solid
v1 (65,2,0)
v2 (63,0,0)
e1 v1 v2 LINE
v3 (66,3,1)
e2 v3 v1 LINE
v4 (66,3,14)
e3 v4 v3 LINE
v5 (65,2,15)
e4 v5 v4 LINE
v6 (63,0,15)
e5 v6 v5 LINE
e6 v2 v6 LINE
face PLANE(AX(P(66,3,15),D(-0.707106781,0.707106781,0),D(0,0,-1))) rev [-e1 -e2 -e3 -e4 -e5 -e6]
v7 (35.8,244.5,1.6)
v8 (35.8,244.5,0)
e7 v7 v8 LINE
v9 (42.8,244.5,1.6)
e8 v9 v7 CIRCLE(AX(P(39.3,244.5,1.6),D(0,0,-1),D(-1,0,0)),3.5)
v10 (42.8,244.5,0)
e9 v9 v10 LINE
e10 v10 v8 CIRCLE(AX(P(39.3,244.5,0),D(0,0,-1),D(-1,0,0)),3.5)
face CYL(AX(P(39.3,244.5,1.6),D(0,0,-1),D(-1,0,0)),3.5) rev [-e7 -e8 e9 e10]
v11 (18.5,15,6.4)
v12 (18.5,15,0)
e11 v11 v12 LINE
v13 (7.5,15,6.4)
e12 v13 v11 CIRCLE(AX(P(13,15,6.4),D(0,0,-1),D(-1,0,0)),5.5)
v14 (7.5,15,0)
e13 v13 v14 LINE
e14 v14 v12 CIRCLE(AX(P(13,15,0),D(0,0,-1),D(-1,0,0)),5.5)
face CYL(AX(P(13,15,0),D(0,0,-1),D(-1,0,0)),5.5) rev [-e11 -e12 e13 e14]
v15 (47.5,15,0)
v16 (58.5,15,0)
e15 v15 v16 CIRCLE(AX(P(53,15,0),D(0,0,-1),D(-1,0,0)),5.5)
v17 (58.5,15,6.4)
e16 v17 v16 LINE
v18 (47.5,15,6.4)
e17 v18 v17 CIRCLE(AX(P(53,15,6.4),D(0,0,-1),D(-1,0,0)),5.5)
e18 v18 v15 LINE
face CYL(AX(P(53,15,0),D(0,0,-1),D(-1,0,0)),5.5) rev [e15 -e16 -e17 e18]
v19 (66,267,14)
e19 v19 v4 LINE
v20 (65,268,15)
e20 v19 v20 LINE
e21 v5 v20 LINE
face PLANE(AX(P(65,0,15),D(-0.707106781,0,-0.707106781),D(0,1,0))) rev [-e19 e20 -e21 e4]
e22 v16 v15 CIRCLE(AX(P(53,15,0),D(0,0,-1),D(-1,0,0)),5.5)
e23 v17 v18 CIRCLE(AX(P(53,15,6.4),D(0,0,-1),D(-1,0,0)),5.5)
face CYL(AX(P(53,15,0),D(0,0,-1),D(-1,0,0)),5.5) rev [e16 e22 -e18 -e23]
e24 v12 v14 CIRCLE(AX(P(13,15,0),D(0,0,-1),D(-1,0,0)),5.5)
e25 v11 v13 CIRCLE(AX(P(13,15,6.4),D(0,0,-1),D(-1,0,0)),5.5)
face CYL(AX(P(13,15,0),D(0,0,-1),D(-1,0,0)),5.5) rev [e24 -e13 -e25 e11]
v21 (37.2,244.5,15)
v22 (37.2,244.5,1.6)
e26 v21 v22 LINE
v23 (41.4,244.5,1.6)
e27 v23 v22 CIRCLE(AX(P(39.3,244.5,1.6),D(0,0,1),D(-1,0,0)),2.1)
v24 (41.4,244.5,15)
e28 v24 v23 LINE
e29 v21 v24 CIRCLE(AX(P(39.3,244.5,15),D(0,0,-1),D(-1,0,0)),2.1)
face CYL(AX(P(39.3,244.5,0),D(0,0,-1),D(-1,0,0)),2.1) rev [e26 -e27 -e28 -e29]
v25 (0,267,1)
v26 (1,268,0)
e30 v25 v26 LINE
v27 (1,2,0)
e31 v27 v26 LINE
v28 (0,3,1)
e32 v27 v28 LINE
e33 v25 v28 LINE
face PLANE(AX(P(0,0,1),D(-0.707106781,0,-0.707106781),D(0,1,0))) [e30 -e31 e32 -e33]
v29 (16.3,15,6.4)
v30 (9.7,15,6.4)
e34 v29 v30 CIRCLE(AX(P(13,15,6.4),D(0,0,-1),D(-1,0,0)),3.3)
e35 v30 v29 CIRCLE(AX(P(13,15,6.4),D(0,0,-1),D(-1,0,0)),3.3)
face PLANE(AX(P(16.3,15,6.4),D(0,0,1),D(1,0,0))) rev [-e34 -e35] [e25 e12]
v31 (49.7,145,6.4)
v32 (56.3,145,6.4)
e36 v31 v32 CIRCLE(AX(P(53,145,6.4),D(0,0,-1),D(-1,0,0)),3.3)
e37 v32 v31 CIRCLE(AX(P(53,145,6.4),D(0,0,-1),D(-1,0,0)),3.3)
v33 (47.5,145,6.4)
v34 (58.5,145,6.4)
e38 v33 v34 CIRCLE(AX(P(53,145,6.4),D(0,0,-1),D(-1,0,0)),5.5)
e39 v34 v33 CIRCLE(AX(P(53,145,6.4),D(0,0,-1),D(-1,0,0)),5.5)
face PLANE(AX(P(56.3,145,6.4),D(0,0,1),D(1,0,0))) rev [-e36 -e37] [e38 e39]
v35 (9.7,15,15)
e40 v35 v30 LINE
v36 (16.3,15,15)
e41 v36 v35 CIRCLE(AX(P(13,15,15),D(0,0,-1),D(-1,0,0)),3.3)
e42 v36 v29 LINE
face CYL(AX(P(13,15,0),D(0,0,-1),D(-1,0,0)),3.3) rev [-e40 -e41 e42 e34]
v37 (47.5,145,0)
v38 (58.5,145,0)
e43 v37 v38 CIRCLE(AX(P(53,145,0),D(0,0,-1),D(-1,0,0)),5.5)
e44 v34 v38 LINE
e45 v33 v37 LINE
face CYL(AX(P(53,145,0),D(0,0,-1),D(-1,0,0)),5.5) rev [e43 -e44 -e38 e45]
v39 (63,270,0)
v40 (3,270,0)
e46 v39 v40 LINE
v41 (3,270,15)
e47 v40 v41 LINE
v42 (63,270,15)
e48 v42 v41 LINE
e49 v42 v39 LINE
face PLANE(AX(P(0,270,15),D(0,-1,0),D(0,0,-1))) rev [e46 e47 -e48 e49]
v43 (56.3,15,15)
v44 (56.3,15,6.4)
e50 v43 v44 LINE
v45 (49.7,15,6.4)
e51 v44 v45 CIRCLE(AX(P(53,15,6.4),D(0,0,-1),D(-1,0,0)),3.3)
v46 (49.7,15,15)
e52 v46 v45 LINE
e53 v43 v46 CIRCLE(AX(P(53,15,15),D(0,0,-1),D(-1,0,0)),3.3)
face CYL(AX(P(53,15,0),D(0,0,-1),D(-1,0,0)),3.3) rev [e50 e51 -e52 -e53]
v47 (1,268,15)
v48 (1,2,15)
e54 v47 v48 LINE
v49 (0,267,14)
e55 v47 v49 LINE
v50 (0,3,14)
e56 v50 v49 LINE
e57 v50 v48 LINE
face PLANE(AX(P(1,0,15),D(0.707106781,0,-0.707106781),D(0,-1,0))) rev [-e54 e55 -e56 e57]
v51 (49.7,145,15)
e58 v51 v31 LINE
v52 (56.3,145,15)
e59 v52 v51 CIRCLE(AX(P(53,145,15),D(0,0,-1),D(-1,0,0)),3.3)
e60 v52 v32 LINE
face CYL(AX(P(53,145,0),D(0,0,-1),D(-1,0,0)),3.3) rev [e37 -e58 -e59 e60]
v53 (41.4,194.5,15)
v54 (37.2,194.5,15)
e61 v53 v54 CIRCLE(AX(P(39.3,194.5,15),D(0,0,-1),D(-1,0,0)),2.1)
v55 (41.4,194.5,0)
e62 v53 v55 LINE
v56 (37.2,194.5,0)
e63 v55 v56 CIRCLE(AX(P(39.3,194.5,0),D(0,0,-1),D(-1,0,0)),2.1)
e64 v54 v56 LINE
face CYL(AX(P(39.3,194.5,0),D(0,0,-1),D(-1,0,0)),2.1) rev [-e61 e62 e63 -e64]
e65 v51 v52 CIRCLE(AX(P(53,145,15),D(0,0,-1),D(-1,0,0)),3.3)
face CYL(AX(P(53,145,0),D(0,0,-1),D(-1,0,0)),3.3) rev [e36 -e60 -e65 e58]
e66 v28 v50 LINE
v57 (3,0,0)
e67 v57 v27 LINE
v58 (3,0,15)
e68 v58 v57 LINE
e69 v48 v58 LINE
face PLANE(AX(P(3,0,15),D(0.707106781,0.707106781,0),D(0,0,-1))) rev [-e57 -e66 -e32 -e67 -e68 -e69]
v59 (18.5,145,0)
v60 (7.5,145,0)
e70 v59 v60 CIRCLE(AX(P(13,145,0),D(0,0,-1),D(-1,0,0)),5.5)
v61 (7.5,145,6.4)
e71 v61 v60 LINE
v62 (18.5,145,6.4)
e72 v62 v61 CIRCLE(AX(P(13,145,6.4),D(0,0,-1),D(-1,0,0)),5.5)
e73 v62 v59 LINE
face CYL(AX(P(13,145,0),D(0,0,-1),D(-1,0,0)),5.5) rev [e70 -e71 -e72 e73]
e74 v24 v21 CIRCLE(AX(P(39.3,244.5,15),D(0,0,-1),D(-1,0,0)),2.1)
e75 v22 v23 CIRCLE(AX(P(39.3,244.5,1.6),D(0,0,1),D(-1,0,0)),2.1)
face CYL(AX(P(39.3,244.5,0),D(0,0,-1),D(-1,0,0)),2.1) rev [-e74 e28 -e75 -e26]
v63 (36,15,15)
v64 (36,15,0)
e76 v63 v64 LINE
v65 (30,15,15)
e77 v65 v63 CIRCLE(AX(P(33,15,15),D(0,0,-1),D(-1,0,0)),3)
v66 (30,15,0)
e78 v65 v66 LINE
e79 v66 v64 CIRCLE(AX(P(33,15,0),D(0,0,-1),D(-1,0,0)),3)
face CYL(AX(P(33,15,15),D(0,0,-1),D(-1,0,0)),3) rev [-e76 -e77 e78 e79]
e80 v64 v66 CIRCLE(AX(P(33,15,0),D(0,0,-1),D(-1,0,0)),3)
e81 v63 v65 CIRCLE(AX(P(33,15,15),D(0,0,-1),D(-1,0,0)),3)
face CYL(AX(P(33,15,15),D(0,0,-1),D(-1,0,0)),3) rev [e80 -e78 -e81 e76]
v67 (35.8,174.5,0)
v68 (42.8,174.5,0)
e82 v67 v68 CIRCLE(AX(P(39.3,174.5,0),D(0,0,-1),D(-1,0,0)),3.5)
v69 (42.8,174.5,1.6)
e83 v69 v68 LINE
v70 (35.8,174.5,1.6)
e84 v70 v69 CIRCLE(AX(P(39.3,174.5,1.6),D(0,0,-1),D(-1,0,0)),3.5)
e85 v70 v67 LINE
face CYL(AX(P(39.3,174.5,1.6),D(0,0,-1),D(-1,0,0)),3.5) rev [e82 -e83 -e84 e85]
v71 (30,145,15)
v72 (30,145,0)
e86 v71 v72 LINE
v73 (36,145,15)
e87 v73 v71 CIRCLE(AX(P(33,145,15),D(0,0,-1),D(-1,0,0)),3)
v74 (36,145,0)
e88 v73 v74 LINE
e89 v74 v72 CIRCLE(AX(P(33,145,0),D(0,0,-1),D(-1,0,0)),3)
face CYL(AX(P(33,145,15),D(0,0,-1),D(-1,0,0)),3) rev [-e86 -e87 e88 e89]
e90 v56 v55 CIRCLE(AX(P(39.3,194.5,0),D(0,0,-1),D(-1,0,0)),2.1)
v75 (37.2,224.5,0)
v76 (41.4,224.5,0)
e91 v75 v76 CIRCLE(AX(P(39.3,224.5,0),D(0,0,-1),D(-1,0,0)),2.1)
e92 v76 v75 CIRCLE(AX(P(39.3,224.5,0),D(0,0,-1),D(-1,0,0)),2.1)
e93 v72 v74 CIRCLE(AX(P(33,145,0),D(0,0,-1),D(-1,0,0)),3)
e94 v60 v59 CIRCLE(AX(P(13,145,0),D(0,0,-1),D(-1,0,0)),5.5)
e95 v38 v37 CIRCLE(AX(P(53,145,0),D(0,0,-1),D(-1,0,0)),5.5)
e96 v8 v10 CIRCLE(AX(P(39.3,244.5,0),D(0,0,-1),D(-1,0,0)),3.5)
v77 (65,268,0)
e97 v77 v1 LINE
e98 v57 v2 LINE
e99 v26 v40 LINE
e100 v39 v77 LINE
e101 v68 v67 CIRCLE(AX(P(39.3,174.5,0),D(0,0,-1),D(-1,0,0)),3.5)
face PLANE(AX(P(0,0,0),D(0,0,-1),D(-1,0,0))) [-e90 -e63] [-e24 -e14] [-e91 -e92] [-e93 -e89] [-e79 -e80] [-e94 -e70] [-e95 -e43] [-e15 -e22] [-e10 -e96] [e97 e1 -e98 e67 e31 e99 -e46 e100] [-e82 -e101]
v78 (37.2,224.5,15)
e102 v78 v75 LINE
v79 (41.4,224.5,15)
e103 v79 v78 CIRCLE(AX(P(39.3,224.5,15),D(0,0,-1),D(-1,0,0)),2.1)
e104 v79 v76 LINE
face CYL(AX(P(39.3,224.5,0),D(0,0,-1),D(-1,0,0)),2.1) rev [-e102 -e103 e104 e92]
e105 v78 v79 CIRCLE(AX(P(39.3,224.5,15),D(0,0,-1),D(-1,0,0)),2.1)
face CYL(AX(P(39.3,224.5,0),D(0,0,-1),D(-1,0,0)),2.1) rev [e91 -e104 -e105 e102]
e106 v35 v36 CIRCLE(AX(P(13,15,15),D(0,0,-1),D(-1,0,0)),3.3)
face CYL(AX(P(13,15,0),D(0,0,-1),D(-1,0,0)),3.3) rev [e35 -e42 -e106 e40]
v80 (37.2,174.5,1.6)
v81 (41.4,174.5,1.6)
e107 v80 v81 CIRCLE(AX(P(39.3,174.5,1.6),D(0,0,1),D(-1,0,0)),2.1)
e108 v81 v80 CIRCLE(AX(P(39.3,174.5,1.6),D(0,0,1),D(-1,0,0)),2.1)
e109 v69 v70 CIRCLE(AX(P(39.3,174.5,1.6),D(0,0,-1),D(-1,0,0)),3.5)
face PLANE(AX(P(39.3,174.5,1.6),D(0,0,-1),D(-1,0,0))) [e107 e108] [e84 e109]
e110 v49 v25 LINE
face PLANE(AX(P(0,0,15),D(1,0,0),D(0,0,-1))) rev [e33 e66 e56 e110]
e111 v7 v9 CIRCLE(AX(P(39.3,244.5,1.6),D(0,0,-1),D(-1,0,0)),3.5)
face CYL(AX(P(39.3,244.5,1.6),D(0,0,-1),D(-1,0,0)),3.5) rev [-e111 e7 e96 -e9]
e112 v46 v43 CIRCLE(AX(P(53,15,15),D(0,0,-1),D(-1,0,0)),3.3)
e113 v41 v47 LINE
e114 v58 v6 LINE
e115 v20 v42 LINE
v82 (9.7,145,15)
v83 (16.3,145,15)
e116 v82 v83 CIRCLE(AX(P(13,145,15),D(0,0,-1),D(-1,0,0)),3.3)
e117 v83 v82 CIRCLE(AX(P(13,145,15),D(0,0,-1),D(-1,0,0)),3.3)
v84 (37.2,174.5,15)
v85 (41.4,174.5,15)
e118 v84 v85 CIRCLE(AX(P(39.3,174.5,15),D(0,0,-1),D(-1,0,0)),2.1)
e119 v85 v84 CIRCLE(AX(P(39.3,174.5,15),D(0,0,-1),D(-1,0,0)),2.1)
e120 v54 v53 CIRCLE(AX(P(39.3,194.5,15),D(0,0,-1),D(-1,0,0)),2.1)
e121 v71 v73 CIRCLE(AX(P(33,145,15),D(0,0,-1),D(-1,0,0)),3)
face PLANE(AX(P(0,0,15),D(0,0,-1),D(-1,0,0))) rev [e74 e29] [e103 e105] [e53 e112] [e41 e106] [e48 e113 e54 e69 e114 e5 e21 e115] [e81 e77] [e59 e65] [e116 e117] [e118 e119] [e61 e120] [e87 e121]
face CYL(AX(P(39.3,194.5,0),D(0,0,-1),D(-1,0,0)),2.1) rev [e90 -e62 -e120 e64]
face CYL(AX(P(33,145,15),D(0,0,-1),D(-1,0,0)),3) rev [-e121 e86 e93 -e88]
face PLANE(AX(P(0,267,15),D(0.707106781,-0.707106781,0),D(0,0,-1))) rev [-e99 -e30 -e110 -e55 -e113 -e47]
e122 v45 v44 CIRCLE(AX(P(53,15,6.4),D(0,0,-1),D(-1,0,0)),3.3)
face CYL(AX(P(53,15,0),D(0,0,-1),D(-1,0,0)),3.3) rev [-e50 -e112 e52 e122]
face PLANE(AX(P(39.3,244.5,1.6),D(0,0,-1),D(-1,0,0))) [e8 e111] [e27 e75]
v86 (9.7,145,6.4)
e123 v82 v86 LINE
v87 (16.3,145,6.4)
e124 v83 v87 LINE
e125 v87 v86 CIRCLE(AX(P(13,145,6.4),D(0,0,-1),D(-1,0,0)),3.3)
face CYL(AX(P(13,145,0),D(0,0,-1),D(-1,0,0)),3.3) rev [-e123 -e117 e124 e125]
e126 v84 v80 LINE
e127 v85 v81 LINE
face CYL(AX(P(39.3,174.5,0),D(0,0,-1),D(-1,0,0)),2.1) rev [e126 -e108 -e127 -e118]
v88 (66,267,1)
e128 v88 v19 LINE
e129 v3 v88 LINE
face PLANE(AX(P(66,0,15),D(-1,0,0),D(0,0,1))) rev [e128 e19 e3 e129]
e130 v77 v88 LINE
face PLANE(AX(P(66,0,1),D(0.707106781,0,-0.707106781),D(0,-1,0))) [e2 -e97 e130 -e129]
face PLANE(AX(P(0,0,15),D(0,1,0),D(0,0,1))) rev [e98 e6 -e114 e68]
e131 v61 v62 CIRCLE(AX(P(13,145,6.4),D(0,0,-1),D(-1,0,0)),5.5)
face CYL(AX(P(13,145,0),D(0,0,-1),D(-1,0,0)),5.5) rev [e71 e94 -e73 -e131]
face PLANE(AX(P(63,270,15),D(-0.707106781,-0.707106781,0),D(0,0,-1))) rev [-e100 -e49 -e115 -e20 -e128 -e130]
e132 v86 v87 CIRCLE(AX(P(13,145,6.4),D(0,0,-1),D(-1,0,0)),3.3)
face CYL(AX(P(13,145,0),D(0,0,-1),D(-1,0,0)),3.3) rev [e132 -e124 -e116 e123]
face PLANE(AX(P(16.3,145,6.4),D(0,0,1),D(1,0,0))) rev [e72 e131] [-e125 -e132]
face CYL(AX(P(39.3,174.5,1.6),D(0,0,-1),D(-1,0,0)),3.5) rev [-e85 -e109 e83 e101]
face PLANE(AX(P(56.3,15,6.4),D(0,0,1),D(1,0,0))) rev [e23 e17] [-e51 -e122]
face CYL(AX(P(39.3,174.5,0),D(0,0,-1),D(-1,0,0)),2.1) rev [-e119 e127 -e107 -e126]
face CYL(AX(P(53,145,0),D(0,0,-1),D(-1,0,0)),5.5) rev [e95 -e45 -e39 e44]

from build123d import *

# Parameters (mm, degrees)
SKETCH1_W                                           = 66
SKETCH1_H                                           = 160
BOSS_EXTRUDE1_DEPTH                                 = 15
CBORE_FOR_M6_HEX_SOCKET_HEAD_CAP_SCREW1_D           = 6.6
CBORE_FOR_M6_HEX_SOCKET_HEAD_CAP_SCREW1_CBORE_D     = 11
CBORE_FOR_M6_HEX_SOCKET_HEAD_CAP_SCREW1_CBORE_DEPTH = 6.4
MOVE_FACE1_BY                                       = 110
M5_TAPPED_HOLE1_D                                   = 4.2
SKETCH6_R                                           = 3.5
CUT_EXTRUDE1_DEPTH                                  = 1.6
CHAMFER2_SIZE                                       = 1
CHAMFER1_SIZE                                       = 3
SKETCH12_R                                          = 3
CUT_EXTRUDE2_DEPTH                                  = 279.354091042


with BuildPart() as part:
    # Sketch1 → Boss-Extrude1 (new body)
    with BuildSketch(Plane.XY):
        with Locations((33, 80)):
            Rectangle(SKETCH1_W, SKETCH1_H)
    extrude(amount=BOSS_EXTRUDE1_DEPTH)

    # CBORE for M6 Hex Socket Head Cap Screw1 (through all)
    with Locations(Plane(origin=(0, 0, 0), x_dir=(-1, 0, 0), z_dir=(0, 0, -1))):
        with Locations((-53, 15), (-13, 15), (-53, 145), (-13, 145)):
            CounterBoreHole(CBORE_FOR_M6_HEX_SOCKET_HEAD_CAP_SCREW1_D / 2, CBORE_FOR_M6_HEX_SOCKET_HEAD_CAP_SCREW1_CBORE_D / 2, CBORE_FOR_M6_HEX_SOCKET_HEAD_CAP_SCREW1_CBORE_DEPTH)

    # Move Face1: a face moved outward by 110.0
    extrude(part.faces().sort_by_distance((33, 160, 7.5))[0], amount=MOVE_FACE1_BY, dir=(0, 1, 0))

    # M5 Tapped Hole1 (through all)
    with Locations(Plane(origin=(0, 0, 0), x_dir=(-1, 0, 0), z_dir=(0, 0, -1))):
        with Locations((-39.3, 244.5), (-39.3, 174.5), (-39.3, 224.5), (-39.3, 194.5)):
            Hole(M5_TAPPED_HOLE1_D / 2)

    # Sketch6 → Cut-Extrude1 (cut)
    with BuildSketch(Plane(origin=(0, 0, 0), x_dir=(-1, 0, 0), z_dir=(0, 0, -1))):
        with Locations((-39.3, 244.5)):
            Circle(SKETCH6_R)
        with Locations((-39.3, 174.5)):
            Circle(SKETCH6_R)
    extrude(amount=-CUT_EXTRUDE1_DEPTH, mode=Mode.SUBTRACT)

    # Chamfer2
    chamfer2_edges = [part.edges().sort_by_distance(p)[0] for p in [
        (66, 135, 15),
        (0, 135, 15),
        (66, 135, 0),
        (0, 135, 0),
    ]]
    chamfer(chamfer2_edges, length=CHAMFER2_SIZE)

    # Chamfer1
    chamfer1_edges = [part.edges().sort_by_distance(p)[0] for p in [
        (0, 0, 7.5),
        (66, 0, 7.5),
        (0, 270, 7.5),
        (66, 270, 7.5),
    ]]
    chamfer(chamfer1_edges, length=CHAMFER1_SIZE)

    # Sketch12 → Cut-Extrude2 (cut, through all)
    with BuildSketch(Plane(origin=(0, 0, 0), x_dir=(-1, 0, 0), z_dir=(0, 0, -1))):
        with Locations((-33, 145)):
            Circle(SKETCH12_R)
        with Locations((-33, 15)):
            Circle(SKETCH12_R)
    extrude(amount=-CUT_EXTRUDE2_DEPTH, mode=Mode.SUBTRACT)


solid = part.part
